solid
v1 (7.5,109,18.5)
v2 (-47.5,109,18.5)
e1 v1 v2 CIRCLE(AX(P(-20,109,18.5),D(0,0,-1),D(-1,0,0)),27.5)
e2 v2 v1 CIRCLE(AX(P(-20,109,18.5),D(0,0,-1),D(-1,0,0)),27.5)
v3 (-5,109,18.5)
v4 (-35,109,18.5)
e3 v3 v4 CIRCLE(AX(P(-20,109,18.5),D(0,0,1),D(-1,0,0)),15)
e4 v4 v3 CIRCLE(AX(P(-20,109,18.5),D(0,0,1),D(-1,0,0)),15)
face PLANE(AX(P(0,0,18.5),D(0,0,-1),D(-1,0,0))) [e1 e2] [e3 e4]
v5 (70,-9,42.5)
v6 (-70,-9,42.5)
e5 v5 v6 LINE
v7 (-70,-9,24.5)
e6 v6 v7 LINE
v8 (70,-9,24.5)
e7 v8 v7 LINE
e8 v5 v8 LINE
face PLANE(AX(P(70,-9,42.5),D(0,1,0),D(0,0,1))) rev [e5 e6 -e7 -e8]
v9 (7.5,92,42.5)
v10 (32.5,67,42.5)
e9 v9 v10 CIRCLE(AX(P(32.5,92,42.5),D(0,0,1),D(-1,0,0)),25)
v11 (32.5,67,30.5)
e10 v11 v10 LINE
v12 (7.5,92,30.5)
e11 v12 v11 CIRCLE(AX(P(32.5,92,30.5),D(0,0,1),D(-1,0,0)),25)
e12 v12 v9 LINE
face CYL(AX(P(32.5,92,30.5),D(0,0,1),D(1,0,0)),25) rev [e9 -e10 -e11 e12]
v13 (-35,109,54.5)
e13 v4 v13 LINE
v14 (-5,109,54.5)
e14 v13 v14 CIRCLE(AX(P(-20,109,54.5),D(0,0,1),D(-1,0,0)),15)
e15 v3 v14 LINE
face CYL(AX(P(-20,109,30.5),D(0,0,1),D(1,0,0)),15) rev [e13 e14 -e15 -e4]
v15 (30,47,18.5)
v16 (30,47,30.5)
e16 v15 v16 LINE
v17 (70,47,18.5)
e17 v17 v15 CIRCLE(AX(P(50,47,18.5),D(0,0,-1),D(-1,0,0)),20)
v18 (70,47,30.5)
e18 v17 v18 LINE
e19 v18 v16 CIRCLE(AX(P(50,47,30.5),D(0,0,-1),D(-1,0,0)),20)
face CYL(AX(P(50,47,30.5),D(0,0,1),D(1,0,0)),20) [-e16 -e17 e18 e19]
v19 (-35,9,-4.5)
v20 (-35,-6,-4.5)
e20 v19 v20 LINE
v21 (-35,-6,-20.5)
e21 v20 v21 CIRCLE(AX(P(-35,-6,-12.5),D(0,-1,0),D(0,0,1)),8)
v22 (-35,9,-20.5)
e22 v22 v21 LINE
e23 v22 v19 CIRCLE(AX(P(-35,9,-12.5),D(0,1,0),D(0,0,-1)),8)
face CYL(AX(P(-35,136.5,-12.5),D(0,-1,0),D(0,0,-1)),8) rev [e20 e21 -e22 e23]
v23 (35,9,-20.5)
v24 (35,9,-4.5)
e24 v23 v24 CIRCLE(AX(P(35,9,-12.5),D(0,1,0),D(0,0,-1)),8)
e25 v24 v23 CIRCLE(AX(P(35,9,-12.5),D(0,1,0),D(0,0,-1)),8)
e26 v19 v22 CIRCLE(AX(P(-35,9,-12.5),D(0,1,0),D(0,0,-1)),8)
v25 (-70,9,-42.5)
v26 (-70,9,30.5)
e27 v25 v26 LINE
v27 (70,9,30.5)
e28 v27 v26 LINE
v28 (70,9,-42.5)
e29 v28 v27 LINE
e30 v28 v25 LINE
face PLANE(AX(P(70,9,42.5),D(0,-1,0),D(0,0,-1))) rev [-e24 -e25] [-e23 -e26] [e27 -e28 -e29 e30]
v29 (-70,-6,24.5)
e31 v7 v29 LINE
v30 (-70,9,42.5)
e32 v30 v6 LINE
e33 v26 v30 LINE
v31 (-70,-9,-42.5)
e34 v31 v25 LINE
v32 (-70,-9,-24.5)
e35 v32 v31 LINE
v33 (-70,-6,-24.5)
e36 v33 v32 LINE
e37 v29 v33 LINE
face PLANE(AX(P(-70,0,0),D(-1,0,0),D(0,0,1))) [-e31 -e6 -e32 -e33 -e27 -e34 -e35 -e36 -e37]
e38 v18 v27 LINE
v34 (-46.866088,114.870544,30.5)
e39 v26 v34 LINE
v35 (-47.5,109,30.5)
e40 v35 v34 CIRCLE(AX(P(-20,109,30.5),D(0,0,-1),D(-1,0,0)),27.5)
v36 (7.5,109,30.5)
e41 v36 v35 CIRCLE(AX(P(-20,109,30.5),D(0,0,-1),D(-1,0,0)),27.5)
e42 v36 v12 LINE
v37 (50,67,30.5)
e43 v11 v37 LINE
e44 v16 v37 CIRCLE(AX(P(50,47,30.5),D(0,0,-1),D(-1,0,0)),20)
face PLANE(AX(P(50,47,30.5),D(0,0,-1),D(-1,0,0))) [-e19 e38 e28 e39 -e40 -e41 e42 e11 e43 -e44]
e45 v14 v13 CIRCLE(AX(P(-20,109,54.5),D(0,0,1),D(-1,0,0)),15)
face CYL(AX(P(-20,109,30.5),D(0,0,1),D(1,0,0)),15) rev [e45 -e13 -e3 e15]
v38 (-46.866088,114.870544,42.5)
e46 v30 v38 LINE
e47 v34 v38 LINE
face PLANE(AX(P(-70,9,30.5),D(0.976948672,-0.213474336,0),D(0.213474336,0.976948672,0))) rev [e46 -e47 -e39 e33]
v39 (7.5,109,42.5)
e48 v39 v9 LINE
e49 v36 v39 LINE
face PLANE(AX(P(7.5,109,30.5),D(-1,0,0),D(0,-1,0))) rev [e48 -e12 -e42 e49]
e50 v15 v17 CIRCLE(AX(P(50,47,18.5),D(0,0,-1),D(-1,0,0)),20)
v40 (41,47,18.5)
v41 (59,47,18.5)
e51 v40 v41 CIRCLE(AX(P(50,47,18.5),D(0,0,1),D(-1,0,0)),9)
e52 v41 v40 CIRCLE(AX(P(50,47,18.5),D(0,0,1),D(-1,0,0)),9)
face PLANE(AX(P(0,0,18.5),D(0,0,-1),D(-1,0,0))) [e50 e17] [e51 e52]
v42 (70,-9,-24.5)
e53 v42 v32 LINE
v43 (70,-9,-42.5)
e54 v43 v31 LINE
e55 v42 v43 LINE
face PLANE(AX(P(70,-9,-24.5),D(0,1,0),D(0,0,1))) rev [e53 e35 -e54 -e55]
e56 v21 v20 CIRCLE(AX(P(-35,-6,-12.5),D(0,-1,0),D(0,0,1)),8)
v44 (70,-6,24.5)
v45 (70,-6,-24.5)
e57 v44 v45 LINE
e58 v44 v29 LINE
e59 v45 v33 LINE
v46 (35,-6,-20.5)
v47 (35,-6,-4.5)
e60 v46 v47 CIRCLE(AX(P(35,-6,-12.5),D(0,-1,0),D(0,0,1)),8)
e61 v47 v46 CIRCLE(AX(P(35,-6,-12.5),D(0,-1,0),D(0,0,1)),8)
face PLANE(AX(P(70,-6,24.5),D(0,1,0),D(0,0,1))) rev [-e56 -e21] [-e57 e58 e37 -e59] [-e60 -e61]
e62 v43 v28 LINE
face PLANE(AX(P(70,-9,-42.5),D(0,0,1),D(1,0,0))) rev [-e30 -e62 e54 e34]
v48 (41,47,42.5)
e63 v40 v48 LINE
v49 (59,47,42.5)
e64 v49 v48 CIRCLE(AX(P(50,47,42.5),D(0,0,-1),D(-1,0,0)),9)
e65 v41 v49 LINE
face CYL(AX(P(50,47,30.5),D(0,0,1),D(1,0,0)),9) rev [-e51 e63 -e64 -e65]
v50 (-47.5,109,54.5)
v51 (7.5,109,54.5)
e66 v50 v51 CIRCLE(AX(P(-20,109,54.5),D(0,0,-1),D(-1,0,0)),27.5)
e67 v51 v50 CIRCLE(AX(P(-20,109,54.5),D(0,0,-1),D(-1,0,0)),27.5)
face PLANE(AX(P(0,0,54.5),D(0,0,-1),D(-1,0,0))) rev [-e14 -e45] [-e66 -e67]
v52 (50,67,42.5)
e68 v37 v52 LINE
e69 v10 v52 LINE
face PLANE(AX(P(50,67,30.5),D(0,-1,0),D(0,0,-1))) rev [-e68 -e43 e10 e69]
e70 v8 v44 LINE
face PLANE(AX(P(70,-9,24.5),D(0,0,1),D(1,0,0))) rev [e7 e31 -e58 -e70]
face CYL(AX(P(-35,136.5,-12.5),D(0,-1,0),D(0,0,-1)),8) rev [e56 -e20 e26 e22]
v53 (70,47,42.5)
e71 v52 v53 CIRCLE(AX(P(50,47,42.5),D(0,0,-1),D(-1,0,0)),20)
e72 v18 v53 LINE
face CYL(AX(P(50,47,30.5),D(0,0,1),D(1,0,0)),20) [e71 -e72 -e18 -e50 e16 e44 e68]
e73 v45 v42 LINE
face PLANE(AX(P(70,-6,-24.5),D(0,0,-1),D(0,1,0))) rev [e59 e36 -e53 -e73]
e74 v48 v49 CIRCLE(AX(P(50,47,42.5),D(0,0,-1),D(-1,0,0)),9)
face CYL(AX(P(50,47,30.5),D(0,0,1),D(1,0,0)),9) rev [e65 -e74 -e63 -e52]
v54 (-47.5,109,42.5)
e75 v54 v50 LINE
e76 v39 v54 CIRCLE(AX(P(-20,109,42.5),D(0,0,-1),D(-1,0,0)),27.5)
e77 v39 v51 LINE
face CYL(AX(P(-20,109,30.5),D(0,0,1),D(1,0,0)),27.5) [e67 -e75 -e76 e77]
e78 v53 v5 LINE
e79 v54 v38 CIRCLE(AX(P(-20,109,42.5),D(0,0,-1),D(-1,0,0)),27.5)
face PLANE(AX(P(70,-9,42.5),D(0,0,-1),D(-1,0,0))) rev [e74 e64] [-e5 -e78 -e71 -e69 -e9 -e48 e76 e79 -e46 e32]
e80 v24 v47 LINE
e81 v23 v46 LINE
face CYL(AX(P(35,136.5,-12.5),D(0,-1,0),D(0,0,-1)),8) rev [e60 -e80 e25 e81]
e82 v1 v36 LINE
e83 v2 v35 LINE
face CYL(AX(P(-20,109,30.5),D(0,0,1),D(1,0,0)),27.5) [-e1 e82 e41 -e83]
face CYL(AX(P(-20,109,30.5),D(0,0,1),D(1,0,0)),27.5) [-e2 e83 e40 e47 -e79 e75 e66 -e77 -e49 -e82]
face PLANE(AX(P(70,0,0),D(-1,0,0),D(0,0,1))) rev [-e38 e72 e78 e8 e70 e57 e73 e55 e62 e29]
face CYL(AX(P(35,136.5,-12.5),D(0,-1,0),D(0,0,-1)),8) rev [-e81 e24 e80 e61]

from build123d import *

# Parameters (mm, degrees)
BASE_ANGLE_DEPTH           = 70
PILLAR_WEB_SKETCH_R        = 15
PILLAR_WEB_SKETCH_R_2      = 9
PILLAR_WEB_DEPTH           = 12
BOSS_PROFILES_SKETCH_R     = 9
UPPER_BEARING_BOSS_DEPTH   = 12
LOWER_HUB_BOSS_DEPTH       = 12
LOWER_HUB_BOSS_DEPTH_BACK  = 24
SKETCH5_5_R                = 15
BASE_CUT_REACH             = 157.327
BASE_CUT_SKETCH_R          = 8
BASE_CUT_DIRECTION_2_DEPTH = 156.327074266


with BuildPart() as part:
    # Base Angle Profile Sketch → Base Angle (new, symmetric)
    with BuildSketch(Plane(origin=(0, 0, 0), x_dir=(0, 0, -1), z_dir=(1, 0, 0))):
        Polygon((-24.5, -9), (-24.5, -6), (24.5, -6), (24.5, -9), (42.5, -9), (42.5, 9), (-42.5, 9), (-42.5, -9), align=None)
    extrude(amount=BASE_ANGLE_DEPTH, both=True)

    # Pillar Web Sketch → Pillar Web (add)
    with BuildSketch(Plane(origin=(0, 0, 42.5), x_dir=(-1, 0, 0), z_dir=(0, 0, -1))):
        with BuildLine():
            Line((-70, 47), (-70, 9))
            Line((-70, 9), (70, 9))
            Line((70, 9), (46.866088482, 114.870544241))
            ThreePointArc((46.866088482, 114.870544241), (17.047664759, 136.341062829), (-7.5, 109))
            Line((-7.5, 109), (-7.5, 92))
            ThreePointArc((-7.5, 92), (-14.82233047, 74.32233047), (-32.5, 67))
            Line((-32.5, 67), (-50, 67))
            ThreePointArc((-50, 67), (-64.142135624, 61.142135624), (-70, 47))
        make_face()
        with Locations((20, 109)):
            Circle(PILLAR_WEB_SKETCH_R, mode=Mode.SUBTRACT)
        with Locations((-50, 47)):
            Circle(PILLAR_WEB_SKETCH_R_2, mode=Mode.SUBTRACT)
    extrude(amount=PILLAR_WEB_DEPTH)

    # Boss Profiles Sketch → Upper Bearing Boss (add)
    with BuildSketch(Plane(origin=(0, 0, 30.5), x_dir=(-1, 0, 0), z_dir=(0, 0, -1))):
        with BuildLine():
            ThreePointArc((-70, 47), (-50, 27), (-30, 47))
            ThreePointArc((-30, 47), (-35.857864376, 61.142135624), (-50, 67))
            ThreePointArc((-50, 67), (-64.142135624, 61.142135624), (-70, 47))
        make_face()
        with Locations((-50, 47)):
            Circle(BOSS_PROFILES_SKETCH_R, mode=Mode.SUBTRACT)
    extrude(amount=UPPER_BEARING_BOSS_DEPTH)

    # Sketch5_5 → Lower Hub Boss (add, two sides: drawn at the far end of the back side and taken through both)
    with BuildSketch(Plane(origin=(0, 0, 30.5), x_dir=(-1, 0, 0), z_dir=(0, 0, -1)).offset(-LOWER_HUB_BOSS_DEPTH_BACK)):
        with BuildLine():
            ThreePointArc((-7.5, 109), (20, 81.5), (47.5, 109))
            ThreePointArc((47.5, 109), (47.341062829, 111.952335241), (46.866088482, 114.870544241))
            ThreePointArc((46.866088482, 114.870544241), (17.047664759, 136.341062829), (-7.5, 109))
        make_face()
        with Locations((20, 109)):
            Circle(SKETCH5_5_R, mode=Mode.SUBTRACT)
    extrude(amount=LOWER_HUB_BOSS_DEPTH + LOWER_HUB_BOSS_DEPTH_BACK)

    # Base Cut Sketch → Base Cut (cut, up to next)
    with BuildSketch(Plane(origin=(0, 9, 0), x_dir=(1, 0, 0), z_dir=(0, 1, 0)), mode=Mode.PRIVATE) as base_cut_sk1:
        with Locations(Location((-35, 12.5, 0), (0, 0, 90))):
            Circle(BASE_CUT_SKETCH_R)
    base_cut_tool1 = extrude(base_cut_sk1.sketch, amount=-BASE_CUT_REACH, mode=Mode.PRIVATE) & part.part
    # Base Cut Sketch → Base Cut (cut, up to next)
    with BuildSketch(Plane(origin=(0, 9, 0), x_dir=(1, 0, 0), z_dir=(0, 1, 0)), mode=Mode.PRIVATE) as base_cut_sk2:
        with Locations(Location((35, 12.5, 0), (0, 0, 90))):
            Circle(BASE_CUT_SKETCH_R)
    base_cut_tool2 = extrude(base_cut_sk2.sketch, amount=-BASE_CUT_REACH, mode=Mode.PRIVATE) & part.part
    add(base_cut_tool1.solids().sort_by_distance((-35, 9, -12.5))[0], mode=Mode.SUBTRACT)
    add(base_cut_tool2.solids().sort_by_distance((35, 9, -12.5))[0], mode=Mode.SUBTRACT)

    # Base Cut Sketch → Base Cut direction 2 (cut)
    with BuildSketch(Plane(origin=(0, 9, 0), x_dir=(1, 0, 0), z_dir=(0, 1, 0))):
        with Locations(Location((-35, 12.5, 0), (0, 0, 90))):
            Circle(BASE_CUT_SKETCH_R)
        with Locations(Location((35, 12.5, 0), (0, 0, 90))):
            Circle(BASE_CUT_SKETCH_R)
    extrude(amount=BASE_CUT_DIRECTION_2_DEPTH, mode=Mode.SUBTRACT)


solid = part.part
